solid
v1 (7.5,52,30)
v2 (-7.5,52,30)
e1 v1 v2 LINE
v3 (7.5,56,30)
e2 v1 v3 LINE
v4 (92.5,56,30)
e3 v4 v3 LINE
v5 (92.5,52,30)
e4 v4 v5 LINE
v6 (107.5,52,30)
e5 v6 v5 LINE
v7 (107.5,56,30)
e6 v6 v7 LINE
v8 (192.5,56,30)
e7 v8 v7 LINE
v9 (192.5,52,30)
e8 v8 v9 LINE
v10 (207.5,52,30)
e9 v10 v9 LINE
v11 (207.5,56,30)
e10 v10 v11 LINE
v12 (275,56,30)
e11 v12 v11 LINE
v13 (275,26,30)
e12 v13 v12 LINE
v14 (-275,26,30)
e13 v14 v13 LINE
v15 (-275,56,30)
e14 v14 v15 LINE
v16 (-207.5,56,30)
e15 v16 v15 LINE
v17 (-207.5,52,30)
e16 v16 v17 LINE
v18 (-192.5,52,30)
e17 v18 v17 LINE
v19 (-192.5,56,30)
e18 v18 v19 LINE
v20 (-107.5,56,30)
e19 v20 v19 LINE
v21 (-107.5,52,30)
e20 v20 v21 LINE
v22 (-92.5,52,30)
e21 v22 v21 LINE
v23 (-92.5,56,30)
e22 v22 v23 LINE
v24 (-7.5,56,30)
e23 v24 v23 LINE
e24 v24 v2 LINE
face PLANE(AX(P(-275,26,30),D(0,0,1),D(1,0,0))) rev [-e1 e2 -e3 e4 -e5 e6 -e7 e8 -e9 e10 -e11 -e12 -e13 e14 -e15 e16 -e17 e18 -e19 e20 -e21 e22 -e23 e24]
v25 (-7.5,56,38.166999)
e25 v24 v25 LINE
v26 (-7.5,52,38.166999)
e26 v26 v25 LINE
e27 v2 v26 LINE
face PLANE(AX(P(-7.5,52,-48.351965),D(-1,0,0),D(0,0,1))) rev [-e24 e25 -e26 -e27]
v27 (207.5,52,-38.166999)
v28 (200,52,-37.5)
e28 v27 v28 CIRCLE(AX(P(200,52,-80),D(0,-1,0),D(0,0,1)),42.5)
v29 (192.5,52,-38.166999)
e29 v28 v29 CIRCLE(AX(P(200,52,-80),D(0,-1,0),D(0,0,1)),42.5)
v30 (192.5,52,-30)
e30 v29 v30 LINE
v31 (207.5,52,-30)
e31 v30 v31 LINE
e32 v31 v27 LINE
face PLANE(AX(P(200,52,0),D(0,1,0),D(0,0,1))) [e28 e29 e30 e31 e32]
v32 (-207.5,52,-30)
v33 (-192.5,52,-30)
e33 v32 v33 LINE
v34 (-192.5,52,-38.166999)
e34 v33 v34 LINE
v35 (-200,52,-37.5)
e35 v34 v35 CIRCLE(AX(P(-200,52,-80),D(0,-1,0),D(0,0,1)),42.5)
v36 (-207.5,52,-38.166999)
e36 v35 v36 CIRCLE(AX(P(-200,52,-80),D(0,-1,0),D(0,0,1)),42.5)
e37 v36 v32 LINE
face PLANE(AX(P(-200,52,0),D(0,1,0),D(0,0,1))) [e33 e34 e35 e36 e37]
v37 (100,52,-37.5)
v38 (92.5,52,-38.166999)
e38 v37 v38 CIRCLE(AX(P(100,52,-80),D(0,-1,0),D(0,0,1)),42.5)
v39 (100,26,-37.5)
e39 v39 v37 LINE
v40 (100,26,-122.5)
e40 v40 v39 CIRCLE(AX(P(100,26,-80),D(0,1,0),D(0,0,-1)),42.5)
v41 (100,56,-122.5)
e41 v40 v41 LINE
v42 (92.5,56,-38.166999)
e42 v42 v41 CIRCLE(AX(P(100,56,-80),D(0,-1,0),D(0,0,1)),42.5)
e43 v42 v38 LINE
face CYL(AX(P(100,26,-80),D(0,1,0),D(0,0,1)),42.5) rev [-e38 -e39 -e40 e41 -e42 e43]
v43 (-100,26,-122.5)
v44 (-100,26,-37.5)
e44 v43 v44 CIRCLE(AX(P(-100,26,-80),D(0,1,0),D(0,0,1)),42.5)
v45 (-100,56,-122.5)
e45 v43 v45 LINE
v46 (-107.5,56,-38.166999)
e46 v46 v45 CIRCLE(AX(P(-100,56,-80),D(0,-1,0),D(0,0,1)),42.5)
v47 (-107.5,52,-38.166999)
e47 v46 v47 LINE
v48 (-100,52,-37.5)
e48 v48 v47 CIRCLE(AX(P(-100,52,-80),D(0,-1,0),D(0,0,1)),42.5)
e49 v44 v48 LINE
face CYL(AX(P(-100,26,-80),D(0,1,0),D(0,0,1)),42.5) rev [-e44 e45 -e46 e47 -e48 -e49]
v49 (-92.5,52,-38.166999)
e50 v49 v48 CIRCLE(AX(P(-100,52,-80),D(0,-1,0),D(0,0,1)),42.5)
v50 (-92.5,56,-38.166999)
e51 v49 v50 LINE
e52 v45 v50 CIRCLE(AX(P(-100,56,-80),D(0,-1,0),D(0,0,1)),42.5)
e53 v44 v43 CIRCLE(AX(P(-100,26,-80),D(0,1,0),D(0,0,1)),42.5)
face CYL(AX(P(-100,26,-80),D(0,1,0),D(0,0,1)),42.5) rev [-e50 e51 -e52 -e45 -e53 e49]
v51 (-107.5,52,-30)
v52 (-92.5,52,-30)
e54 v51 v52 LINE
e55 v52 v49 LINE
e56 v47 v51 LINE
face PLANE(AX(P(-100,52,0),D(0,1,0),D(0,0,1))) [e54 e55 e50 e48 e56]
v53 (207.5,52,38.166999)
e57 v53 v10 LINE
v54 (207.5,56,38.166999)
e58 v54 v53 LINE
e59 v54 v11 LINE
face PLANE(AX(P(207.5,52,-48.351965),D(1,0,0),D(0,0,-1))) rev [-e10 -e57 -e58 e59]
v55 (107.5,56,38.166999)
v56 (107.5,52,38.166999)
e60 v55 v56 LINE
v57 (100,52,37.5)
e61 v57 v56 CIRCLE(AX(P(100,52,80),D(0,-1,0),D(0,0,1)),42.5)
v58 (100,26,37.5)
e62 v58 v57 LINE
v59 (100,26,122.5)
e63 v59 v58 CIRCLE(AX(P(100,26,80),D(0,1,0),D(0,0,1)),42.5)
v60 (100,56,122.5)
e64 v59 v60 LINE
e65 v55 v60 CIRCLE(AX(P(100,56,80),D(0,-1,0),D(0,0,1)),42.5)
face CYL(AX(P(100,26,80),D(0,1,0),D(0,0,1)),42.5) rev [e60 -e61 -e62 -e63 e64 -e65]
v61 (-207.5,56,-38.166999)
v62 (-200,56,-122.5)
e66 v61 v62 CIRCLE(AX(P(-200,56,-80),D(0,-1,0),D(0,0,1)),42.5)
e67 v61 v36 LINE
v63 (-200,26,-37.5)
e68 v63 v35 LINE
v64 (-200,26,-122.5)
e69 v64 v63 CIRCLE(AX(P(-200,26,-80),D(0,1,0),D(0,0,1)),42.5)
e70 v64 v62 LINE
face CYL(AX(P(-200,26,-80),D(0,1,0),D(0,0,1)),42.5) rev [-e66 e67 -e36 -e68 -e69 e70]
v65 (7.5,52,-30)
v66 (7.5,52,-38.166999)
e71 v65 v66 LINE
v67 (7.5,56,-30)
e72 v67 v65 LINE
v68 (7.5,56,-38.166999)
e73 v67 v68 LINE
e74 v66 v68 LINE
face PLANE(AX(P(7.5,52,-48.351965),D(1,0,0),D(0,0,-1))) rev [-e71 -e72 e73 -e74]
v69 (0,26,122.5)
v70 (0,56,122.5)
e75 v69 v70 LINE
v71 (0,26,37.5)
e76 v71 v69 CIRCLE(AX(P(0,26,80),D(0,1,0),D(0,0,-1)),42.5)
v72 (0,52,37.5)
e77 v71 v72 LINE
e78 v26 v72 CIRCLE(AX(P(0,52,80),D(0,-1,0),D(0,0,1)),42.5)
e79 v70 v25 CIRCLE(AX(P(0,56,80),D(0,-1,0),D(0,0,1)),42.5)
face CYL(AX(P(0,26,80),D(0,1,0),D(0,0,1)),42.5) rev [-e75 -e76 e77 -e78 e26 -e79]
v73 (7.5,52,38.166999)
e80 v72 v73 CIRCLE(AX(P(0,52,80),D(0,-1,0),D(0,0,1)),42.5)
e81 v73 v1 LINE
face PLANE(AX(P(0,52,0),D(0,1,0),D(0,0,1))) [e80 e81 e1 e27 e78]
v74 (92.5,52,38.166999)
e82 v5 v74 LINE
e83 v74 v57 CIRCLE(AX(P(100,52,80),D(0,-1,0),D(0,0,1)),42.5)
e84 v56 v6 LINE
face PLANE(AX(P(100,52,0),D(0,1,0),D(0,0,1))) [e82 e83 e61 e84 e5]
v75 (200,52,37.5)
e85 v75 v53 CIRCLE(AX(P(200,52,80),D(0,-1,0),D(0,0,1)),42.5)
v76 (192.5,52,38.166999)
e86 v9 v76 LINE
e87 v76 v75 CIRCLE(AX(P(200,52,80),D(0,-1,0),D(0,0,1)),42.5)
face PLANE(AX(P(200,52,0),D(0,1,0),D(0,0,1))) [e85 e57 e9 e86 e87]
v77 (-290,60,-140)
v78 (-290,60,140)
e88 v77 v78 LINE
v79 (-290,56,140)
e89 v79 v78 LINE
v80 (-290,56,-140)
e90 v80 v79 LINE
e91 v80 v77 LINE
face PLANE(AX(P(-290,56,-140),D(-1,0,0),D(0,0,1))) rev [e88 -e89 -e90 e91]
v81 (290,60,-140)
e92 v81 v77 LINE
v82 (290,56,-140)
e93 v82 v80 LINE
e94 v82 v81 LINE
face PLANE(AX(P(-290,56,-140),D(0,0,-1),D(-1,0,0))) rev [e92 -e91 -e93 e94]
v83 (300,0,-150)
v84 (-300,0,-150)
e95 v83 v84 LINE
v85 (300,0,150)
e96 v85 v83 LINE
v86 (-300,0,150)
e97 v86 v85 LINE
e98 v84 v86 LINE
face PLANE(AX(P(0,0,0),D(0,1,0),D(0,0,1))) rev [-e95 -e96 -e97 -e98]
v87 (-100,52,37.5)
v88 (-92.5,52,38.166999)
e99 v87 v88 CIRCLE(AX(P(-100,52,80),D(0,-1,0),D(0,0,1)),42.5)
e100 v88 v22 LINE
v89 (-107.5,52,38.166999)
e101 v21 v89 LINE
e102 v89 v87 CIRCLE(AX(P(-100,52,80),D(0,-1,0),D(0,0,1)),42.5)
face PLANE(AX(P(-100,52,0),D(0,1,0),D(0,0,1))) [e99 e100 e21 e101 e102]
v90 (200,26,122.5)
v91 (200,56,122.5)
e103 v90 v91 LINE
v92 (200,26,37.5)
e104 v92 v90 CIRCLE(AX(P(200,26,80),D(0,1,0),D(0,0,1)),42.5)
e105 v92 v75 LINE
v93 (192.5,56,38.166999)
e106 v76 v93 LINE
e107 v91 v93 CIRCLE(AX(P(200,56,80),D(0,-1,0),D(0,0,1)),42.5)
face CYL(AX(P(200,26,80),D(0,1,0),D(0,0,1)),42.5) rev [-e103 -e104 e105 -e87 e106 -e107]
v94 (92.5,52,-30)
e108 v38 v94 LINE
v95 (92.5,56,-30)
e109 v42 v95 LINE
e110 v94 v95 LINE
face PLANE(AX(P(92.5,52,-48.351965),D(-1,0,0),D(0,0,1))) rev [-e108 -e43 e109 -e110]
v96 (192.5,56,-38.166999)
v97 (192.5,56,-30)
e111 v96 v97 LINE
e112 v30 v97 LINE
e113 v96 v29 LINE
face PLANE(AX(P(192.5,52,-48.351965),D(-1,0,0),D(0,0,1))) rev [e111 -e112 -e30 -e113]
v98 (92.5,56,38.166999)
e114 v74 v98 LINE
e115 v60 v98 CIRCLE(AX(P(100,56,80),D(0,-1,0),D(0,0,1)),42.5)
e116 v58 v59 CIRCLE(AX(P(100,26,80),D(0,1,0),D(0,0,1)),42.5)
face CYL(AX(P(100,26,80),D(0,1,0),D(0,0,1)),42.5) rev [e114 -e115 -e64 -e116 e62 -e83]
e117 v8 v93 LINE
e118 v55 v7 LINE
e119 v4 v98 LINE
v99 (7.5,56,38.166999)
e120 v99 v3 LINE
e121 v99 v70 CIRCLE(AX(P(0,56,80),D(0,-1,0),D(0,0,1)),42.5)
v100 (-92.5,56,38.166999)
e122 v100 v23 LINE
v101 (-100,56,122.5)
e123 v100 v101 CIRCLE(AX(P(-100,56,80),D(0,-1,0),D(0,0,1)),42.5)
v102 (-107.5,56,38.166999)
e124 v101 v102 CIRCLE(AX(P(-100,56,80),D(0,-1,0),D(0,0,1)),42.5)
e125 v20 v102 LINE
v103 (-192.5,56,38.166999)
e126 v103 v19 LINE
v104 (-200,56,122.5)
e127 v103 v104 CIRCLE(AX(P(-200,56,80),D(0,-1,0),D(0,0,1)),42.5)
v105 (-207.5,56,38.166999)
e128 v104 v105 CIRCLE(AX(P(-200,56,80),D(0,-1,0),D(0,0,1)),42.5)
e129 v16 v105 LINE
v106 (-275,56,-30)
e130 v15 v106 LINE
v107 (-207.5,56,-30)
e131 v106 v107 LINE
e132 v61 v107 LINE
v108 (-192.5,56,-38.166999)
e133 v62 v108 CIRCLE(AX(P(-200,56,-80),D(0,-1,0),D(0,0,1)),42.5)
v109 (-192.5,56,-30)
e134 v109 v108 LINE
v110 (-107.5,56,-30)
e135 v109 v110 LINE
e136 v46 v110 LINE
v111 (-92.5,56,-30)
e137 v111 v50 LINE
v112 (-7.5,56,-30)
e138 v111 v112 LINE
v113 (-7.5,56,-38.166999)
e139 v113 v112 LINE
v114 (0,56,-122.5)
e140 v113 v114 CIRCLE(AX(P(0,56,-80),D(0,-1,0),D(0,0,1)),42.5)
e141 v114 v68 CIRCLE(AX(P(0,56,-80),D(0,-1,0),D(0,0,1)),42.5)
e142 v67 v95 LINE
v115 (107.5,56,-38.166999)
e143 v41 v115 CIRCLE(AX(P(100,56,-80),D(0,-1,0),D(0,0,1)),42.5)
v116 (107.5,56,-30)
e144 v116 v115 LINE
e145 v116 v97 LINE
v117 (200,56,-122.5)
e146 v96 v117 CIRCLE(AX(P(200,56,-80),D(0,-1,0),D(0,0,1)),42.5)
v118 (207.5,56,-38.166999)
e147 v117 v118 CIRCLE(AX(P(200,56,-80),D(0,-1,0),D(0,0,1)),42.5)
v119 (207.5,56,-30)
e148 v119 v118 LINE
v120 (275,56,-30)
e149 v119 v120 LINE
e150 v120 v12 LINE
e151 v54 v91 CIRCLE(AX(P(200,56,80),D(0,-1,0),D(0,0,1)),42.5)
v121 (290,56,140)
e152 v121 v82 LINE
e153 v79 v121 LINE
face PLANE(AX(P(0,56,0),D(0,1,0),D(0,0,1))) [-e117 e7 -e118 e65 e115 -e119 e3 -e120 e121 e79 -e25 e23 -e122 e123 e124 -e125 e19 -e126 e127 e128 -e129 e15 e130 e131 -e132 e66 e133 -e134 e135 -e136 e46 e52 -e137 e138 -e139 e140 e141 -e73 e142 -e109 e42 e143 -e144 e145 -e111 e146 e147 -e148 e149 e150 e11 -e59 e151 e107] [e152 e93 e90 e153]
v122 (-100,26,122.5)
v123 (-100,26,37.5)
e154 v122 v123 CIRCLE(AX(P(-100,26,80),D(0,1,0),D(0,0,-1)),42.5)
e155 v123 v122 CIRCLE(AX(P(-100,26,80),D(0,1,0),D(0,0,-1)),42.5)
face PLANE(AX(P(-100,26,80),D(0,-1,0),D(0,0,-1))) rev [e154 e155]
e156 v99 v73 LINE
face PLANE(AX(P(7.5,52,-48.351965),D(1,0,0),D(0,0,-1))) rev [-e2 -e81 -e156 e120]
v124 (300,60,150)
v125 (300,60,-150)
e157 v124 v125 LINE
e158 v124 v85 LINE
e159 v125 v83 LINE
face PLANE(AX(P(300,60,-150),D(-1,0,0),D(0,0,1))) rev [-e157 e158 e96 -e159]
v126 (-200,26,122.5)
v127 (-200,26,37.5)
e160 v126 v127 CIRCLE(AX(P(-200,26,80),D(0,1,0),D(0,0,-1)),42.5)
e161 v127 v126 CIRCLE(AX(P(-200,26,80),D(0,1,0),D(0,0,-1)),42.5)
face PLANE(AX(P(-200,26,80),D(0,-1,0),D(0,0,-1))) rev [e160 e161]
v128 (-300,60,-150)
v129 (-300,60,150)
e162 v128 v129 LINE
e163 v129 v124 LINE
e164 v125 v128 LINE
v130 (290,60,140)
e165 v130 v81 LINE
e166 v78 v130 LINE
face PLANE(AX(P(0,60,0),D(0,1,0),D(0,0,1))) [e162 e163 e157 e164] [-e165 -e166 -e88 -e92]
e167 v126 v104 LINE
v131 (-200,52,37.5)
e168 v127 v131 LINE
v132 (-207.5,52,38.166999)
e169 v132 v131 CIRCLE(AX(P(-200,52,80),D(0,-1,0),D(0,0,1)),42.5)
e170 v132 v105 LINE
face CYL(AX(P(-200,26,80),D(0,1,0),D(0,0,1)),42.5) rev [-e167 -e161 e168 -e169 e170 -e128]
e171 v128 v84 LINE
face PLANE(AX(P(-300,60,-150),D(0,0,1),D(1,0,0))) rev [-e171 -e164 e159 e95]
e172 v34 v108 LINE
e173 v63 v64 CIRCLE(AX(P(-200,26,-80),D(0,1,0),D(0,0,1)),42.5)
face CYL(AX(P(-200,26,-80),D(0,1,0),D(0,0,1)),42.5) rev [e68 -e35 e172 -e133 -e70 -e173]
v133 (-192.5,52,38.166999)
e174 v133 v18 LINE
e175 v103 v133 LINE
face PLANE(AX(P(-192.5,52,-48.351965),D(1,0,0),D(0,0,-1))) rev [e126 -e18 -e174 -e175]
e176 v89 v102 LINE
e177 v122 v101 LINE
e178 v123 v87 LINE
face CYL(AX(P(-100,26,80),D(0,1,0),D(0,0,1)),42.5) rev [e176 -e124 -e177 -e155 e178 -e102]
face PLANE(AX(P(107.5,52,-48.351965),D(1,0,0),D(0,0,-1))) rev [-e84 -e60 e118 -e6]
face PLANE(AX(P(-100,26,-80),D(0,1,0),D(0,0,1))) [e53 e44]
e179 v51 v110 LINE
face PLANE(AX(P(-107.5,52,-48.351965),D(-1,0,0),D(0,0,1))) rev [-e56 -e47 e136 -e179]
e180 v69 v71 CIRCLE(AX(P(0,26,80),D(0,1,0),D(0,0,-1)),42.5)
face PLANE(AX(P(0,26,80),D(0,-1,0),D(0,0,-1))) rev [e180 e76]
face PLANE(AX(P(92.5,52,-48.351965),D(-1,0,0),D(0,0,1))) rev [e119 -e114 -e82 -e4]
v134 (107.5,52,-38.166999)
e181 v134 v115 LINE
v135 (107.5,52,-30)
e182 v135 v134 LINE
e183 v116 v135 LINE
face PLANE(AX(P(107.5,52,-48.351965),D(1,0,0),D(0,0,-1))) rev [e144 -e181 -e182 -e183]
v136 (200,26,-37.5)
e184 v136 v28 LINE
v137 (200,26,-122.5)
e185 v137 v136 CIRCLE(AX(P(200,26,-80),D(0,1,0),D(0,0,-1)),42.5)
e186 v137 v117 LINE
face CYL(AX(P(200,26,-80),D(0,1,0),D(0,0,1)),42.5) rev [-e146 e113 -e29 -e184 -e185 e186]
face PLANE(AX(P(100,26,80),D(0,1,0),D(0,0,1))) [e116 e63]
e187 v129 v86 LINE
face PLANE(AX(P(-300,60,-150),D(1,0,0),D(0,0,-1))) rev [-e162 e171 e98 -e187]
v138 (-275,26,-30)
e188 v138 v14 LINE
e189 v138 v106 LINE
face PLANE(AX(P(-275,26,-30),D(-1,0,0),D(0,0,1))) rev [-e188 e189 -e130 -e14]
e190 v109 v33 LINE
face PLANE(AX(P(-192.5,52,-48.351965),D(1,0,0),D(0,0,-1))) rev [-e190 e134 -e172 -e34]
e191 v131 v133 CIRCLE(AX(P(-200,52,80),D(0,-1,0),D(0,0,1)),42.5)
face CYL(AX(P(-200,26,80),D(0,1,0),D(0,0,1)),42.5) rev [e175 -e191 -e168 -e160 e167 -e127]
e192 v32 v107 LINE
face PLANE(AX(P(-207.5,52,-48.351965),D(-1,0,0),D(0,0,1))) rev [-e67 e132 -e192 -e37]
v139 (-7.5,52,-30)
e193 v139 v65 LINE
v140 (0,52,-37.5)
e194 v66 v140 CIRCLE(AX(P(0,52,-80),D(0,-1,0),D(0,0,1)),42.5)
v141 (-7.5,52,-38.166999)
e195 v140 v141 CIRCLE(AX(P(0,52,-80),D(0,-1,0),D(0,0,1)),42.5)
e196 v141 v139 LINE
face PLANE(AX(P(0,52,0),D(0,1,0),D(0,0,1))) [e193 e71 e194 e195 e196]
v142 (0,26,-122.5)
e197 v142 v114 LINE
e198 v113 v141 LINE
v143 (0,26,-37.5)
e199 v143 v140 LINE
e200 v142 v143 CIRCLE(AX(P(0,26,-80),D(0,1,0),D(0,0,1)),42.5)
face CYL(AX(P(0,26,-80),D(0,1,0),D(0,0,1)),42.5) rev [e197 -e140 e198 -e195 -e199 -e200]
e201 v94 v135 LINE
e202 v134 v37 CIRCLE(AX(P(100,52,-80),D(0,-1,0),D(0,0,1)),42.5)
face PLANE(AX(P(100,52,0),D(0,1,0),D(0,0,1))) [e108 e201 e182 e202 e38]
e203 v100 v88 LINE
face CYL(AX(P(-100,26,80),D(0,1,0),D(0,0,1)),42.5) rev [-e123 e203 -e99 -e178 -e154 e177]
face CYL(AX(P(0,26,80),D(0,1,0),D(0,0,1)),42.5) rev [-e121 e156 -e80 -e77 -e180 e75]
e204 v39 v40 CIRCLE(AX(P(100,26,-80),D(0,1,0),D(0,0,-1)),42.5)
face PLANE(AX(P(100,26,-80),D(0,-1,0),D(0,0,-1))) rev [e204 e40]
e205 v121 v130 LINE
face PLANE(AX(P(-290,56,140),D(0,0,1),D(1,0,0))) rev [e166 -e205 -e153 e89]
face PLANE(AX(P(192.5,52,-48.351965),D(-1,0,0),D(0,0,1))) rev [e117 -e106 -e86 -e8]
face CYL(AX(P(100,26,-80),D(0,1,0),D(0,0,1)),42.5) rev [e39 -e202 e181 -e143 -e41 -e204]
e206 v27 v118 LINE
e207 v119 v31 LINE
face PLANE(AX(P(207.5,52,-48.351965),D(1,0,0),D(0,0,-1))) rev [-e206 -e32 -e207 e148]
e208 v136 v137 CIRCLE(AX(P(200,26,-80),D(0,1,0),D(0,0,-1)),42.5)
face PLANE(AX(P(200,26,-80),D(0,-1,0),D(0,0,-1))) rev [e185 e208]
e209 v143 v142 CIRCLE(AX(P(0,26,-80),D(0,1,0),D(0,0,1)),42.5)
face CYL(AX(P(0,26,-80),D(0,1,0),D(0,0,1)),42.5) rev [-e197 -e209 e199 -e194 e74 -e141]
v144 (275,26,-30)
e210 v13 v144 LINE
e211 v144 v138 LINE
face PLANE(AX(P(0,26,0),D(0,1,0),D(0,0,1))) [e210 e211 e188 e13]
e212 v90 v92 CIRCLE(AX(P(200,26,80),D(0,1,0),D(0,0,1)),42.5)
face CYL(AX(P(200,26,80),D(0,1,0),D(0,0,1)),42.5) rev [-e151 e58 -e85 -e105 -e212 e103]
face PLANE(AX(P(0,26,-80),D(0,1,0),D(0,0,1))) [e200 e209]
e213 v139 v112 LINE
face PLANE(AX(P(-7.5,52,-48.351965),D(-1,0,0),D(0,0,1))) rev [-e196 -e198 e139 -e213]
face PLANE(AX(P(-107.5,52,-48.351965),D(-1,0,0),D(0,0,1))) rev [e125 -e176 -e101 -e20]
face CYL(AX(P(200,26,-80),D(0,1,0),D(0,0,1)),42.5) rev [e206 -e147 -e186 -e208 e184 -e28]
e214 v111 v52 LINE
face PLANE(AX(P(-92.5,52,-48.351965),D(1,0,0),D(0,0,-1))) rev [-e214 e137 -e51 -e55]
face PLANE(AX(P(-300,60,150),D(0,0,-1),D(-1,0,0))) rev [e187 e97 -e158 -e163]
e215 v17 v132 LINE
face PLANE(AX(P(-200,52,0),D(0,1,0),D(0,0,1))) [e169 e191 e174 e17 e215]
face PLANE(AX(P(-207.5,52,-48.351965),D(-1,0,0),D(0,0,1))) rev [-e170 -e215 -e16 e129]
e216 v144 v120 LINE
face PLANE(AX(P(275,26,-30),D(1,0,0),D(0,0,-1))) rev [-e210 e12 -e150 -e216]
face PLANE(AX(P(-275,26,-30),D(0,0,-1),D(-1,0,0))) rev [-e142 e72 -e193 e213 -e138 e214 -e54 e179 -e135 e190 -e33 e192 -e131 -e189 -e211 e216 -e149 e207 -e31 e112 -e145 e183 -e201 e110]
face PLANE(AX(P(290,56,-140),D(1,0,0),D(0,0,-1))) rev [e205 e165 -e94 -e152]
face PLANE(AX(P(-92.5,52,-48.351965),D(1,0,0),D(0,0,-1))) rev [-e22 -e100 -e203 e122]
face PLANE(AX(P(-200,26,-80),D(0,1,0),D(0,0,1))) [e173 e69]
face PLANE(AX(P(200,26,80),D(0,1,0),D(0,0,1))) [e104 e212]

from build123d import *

# Parameters (mm, degrees)
SKETCH1_W           = 600
SKETCH1_H           = 300
BOSS_EXTRUDE1_DEPTH = 60
SKETCH2_R           = 42.5
SKETCH2_W           = 550
SKETCH2_H           = 60
CUT_EXTRUDE1_DEPTH  = 34
SKETCH3_W           = 580
SKETCH3_H           = 280
CUT_EXTRUDE2_DEPTH  = 4
SKETCH4_W           = 15
SKETCH4_H           = 96.703930486
CUT_EXTRUDE3_DEPTH  = 4
LPATTERN1_COUNT     = 3
LPATTERN1_PITCH     = 100
LPATTERN1_COL_COUNT = 3
LPATTERN1_COL_PITCH = 100


with BuildPart() as part:
    # Sketch1 → Boss-Extrude1 (new body)
    with BuildSketch(Plane(origin=(0, 0, 0), x_dir=(1, 0, 0), z_dir=(0, 1, 0))):
        Rectangle(SKETCH1_W, SKETCH1_H)
    extrude(amount=BOSS_EXTRUDE1_DEPTH)

    # Sketch2 → Cut-Extrude1 (cut)
    with BuildSketch(Plane(origin=(0, 60, 0), x_dir=(1, 0, 0), z_dir=(0, 1, 0))):
        with Locations(Location((0, 80, 0), (0, 0, 270))):
            Circle(SKETCH2_R)
        with Locations(Location((0, -80, 0), (0, 0, 90))):
            Circle(SKETCH2_R)
        with Locations(Location((-100, 80, 0), (0, 0, 270))):
            Circle(SKETCH2_R)
        with Locations(Location((-200, 80, 0), (0, 0, 270))):
            Circle(SKETCH2_R)
        with Locations(Location((200, 80, 0), (0, 0, 90))):
            Circle(SKETCH2_R)
        with Locations(Location((100, 80, 0), (0, 0, 90))):
            Circle(SKETCH2_R)
        with Locations(Location((200, -80, 0), (0, 0, 270))):
            Circle(SKETCH2_R)
        with Locations(Location((100, -80, 0), (0, 0, 270))):
            Circle(SKETCH2_R)
        with Locations(Location((-100, -80, 0), (0, 0, 90))):
            Circle(SKETCH2_R)
        with Locations(Location((-200, -80, 0), (0, 0, 90))):
            Circle(SKETCH2_R)
        Rectangle(SKETCH2_W, SKETCH2_H)
    extrude(amount=-CUT_EXTRUDE1_DEPTH, mode=Mode.SUBTRACT)

    # Sketch3 → Cut-Extrude2 (cut)
    with BuildSketch(Plane(origin=(0, 60, 0), x_dir=(1, 0, 0), z_dir=(0, 1, 0))):
        Rectangle(SKETCH3_W, SKETCH3_H)
    extrude(amount=-CUT_EXTRUDE2_DEPTH, mode=Mode.SUBTRACT)

    # Sketch4 → Cut-Extrude3 (cut)
    with BuildSketch(Plane(origin=(0, 56, 0), x_dir=(1, 0, 0), z_dir=(0, 1, 0))):
        Rectangle(SKETCH4_W, SKETCH4_H)
    cut_extrude3 = extrude(amount=-CUT_EXTRUDE3_DEPTH, mode=Mode.SUBTRACT)

    # LPattern1: Cut-Extrude3 ×3
    with Locations(*[(-i * LPATTERN1_PITCH, 0, 0) for i in range(1, LPATTERN1_COUNT)]):
        add(cut_extrude3, mode=Mode.SUBTRACT)

    # LPattern1 col: Cut-Extrude3 ×3
    with Locations(*[(i * LPATTERN1_COL_PITCH, 0, 0) for i in range(1, LPATTERN1_COL_COUNT)]):
        add(cut_extrude3, mode=Mode.SUBTRACT)


solid = part.part
